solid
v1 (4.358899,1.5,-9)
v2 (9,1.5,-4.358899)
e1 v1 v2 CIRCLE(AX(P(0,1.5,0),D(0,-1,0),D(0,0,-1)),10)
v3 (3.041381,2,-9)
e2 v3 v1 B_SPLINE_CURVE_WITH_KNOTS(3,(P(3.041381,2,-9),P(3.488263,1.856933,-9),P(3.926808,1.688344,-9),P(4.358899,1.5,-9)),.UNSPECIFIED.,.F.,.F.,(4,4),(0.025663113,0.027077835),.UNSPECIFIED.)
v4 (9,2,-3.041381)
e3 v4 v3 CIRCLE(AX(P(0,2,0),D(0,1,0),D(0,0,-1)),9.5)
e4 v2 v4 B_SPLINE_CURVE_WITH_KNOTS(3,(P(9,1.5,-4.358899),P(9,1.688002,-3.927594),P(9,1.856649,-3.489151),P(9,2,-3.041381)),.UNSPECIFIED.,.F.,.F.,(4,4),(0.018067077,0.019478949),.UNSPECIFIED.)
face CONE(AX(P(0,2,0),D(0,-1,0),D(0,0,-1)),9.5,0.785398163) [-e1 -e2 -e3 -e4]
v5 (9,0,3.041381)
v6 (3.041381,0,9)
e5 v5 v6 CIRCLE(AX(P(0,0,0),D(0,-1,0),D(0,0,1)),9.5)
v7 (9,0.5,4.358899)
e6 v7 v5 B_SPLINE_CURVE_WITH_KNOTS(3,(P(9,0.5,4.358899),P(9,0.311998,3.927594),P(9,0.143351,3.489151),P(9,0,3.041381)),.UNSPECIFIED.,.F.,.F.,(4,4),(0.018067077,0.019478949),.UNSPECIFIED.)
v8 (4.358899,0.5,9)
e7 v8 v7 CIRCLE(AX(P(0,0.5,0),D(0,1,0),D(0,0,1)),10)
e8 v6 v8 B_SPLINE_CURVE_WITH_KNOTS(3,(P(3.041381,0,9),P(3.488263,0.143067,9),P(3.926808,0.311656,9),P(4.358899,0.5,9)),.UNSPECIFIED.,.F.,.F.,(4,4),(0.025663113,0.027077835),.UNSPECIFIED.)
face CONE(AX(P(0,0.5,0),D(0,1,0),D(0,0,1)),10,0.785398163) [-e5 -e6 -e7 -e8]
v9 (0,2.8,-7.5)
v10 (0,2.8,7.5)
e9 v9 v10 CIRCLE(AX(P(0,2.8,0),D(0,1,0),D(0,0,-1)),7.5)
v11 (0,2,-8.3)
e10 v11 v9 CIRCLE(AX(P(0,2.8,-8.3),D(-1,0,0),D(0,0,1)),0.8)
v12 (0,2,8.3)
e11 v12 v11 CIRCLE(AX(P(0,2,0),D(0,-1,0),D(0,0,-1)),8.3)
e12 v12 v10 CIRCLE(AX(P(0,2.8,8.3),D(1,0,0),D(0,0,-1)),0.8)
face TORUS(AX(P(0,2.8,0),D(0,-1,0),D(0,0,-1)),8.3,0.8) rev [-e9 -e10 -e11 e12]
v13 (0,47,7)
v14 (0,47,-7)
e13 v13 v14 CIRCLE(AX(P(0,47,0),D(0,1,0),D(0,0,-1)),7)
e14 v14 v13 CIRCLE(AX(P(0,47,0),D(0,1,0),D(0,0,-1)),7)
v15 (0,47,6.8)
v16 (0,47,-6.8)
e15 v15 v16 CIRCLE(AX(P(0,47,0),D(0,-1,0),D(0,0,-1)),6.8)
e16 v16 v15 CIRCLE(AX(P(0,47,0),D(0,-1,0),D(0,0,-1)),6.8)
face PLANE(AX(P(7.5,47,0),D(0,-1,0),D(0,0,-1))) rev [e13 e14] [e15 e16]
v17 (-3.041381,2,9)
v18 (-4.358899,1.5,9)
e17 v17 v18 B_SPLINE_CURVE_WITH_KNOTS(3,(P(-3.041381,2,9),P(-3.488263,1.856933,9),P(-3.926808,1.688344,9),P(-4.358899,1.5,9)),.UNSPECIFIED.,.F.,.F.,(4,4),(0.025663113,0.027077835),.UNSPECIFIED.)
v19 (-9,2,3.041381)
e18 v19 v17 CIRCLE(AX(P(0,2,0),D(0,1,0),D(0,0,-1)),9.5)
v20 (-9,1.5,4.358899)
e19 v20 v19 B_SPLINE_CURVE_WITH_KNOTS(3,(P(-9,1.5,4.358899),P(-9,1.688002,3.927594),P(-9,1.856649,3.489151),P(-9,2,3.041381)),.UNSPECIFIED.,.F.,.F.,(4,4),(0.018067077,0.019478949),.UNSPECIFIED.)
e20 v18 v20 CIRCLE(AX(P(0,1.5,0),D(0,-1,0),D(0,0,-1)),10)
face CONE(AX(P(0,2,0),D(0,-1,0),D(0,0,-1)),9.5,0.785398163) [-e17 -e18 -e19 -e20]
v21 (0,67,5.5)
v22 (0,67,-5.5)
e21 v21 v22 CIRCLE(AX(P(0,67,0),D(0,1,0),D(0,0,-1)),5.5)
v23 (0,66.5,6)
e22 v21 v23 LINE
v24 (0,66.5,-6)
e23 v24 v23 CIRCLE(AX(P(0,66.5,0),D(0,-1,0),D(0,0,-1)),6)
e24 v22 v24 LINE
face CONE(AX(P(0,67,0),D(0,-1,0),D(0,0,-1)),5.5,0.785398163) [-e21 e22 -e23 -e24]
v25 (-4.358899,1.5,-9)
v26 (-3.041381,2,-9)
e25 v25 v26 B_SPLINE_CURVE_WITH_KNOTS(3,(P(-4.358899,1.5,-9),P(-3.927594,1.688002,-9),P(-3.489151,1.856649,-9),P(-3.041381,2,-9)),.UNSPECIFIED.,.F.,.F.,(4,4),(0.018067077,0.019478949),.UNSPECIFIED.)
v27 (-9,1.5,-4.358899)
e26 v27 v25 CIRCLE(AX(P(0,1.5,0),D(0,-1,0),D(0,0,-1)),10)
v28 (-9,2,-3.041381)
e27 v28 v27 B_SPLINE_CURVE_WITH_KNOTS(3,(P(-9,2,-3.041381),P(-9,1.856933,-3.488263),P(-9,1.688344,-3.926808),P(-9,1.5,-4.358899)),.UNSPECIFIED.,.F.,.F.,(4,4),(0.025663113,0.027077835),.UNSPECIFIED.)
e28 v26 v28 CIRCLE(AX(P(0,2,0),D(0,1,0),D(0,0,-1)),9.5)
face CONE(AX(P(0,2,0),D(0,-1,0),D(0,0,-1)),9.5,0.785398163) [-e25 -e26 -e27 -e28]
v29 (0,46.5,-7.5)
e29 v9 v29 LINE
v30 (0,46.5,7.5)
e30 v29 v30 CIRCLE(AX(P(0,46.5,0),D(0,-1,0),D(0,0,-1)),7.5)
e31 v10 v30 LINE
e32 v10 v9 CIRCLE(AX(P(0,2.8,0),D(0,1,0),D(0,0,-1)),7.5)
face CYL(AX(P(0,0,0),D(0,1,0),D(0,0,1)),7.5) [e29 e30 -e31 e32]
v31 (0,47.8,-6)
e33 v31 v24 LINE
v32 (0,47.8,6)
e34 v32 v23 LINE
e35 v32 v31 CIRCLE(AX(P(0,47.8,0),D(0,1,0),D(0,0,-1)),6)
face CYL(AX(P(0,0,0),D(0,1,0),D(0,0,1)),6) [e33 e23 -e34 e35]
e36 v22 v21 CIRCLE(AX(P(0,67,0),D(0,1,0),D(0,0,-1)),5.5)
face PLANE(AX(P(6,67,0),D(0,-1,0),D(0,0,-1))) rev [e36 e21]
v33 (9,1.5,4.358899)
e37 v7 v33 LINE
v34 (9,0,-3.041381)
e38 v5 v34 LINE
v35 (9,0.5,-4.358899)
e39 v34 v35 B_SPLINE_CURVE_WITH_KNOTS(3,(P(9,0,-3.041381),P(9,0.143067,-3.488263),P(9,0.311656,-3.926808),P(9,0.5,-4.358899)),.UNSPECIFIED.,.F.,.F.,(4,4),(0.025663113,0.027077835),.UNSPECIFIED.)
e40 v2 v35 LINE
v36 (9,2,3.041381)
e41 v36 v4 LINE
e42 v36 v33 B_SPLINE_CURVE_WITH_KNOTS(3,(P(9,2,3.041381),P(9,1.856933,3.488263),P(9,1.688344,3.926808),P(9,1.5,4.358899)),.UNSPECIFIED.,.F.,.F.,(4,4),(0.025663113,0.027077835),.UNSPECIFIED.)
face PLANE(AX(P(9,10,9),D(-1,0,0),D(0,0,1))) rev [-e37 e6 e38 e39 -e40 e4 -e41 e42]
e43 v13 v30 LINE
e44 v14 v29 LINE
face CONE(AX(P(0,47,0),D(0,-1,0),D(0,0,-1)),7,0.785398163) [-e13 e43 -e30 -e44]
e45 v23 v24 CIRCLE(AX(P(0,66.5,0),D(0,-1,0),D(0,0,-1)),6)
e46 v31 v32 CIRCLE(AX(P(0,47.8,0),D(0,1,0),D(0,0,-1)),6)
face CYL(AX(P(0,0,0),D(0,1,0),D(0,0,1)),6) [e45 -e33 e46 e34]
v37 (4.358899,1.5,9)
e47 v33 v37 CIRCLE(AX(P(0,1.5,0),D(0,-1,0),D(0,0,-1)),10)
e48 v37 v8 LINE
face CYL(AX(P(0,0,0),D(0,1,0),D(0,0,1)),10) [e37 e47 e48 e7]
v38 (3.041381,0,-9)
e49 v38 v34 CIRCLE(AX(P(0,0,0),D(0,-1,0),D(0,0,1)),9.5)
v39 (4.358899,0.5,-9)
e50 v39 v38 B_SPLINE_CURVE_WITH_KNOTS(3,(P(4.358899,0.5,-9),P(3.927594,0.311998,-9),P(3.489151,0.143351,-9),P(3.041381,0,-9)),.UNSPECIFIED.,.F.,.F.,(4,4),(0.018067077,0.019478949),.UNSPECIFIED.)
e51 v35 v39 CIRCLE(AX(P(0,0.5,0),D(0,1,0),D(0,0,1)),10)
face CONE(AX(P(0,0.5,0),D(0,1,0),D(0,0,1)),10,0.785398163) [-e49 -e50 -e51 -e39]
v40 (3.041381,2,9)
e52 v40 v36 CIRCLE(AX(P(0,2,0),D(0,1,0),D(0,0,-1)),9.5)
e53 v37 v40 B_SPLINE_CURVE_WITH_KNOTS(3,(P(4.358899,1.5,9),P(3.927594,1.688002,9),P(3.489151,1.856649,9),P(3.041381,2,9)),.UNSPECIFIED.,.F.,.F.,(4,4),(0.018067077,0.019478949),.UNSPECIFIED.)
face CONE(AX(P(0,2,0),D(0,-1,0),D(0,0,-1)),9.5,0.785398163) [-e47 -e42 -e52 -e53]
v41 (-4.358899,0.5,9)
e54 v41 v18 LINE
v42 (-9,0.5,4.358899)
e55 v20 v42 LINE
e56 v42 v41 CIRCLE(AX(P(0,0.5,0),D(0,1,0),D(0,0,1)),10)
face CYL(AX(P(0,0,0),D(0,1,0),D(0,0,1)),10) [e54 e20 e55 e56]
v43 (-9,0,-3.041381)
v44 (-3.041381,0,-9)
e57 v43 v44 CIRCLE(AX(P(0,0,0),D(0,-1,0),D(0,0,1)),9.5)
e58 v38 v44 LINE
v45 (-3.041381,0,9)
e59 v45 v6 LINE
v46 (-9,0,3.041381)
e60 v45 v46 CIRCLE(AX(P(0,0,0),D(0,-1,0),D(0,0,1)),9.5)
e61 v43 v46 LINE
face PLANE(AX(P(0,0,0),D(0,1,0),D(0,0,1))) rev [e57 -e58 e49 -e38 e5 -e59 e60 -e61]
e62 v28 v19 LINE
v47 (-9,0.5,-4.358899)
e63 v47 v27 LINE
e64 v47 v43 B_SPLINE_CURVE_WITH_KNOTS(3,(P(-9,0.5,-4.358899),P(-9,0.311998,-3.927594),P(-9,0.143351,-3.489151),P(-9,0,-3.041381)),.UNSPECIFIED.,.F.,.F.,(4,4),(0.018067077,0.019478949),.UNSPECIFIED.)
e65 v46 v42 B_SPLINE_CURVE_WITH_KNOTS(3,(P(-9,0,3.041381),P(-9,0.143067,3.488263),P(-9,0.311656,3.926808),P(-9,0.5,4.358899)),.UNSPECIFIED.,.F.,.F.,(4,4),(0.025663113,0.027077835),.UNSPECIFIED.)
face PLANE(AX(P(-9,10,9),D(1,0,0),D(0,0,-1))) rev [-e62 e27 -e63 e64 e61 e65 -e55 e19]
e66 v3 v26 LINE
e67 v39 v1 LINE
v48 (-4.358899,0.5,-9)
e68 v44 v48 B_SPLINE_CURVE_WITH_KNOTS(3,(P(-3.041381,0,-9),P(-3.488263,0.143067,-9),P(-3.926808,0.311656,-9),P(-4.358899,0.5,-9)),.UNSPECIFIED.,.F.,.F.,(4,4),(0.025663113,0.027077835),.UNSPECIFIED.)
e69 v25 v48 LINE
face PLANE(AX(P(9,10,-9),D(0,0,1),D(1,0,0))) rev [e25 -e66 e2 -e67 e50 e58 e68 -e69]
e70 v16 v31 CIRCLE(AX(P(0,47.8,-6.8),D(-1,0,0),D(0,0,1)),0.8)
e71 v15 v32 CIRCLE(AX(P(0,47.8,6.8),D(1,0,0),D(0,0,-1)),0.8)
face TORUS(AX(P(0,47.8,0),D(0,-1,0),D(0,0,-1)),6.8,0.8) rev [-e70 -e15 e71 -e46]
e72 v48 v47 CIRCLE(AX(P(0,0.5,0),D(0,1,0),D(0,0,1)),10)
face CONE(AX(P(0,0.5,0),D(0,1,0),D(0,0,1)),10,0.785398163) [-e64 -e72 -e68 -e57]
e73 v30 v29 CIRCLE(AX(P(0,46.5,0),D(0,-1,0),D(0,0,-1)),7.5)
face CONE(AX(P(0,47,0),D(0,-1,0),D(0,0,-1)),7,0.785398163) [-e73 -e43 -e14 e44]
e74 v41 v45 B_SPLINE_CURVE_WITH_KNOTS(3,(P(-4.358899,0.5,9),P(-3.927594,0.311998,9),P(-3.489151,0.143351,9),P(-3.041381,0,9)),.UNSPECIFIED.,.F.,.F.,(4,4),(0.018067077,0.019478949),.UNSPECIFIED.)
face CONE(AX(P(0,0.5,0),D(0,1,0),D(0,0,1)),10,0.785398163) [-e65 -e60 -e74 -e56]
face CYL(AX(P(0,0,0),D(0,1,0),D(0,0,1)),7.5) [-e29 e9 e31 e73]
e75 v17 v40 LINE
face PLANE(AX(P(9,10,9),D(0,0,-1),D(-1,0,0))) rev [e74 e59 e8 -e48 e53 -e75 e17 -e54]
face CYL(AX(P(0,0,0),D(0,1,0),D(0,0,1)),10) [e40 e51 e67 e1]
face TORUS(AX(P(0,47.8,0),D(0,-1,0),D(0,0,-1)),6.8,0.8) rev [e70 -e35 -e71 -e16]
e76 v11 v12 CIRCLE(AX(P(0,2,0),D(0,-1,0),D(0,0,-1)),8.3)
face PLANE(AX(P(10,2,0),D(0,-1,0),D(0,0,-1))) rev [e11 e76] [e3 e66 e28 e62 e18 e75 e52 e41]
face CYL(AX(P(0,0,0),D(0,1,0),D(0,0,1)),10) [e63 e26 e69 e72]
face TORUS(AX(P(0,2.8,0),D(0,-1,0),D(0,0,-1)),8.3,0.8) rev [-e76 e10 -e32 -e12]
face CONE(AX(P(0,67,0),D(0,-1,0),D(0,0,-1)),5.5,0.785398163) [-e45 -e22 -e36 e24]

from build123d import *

# Parameters (mm, degrees)
CHAMFER1_SIZE       = 0.5
FILLET1_R           = 0.8
SKETCH2_OUTSIDE_W   = 36.546
SKETCH2_OUTSIDE_H   = 36.546
SKETCH2_OUTSIDE_W_2 = 18
SKETCH2_OUTSIDE_H_2 = 18
CUT_EXTRUDE1_DEPTH  = 10


with BuildPart() as part:
    # Sketch1 → Revolve1 (revolve)
    with BuildSketch(Plane.XY, mode=Mode.PRIVATE) as revolve1_sk:
        Polygon((0, 0), (10, 0), (10, 2), (7.5, 2), (7.5, 47), (6, 47), (6, 67), (0, 67), align=None)
    revolve(revolve1_sk.sketch.rotate(Axis((0, 0, 0), (0, -1, 0)), 90), axis=Axis((0, 0, 0), (0, -1, 0)))

    # Chamfer1
    chamfer1_edges = [part.edges().sort_by_distance(p)[0] for p in [
        (0, 67, -6),
        (0, 47, -7.5),
        (0, 2, -10),
        (0, 0, -10),
    ]]
    chamfer(chamfer1_edges, length=CHAMFER1_SIZE)

    # Fillet1
    fillet1_edges = [part.edges().sort_by_distance(p)[0] for p in [
        (0, 47, -6),
        (0, 2, -7.5),
    ]]
    fillet(fillet1_edges, radius=FILLET1_R)

    # Sketch2 outside → Cut-Extrude1 (cut)
    with BuildSketch(Plane(origin=(0, 0, 0), x_dir=(1, 0, 0), z_dir=(0, 1, 0))):
        Rectangle(SKETCH2_OUTSIDE_W, SKETCH2_OUTSIDE_H)
        Rectangle(SKETCH2_OUTSIDE_W_2, SKETCH2_OUTSIDE_H_2, mode=Mode.SUBTRACT)
    extrude(amount=CUT_EXTRUDE1_DEPTH, mode=Mode.SUBTRACT)


solid = part.part
